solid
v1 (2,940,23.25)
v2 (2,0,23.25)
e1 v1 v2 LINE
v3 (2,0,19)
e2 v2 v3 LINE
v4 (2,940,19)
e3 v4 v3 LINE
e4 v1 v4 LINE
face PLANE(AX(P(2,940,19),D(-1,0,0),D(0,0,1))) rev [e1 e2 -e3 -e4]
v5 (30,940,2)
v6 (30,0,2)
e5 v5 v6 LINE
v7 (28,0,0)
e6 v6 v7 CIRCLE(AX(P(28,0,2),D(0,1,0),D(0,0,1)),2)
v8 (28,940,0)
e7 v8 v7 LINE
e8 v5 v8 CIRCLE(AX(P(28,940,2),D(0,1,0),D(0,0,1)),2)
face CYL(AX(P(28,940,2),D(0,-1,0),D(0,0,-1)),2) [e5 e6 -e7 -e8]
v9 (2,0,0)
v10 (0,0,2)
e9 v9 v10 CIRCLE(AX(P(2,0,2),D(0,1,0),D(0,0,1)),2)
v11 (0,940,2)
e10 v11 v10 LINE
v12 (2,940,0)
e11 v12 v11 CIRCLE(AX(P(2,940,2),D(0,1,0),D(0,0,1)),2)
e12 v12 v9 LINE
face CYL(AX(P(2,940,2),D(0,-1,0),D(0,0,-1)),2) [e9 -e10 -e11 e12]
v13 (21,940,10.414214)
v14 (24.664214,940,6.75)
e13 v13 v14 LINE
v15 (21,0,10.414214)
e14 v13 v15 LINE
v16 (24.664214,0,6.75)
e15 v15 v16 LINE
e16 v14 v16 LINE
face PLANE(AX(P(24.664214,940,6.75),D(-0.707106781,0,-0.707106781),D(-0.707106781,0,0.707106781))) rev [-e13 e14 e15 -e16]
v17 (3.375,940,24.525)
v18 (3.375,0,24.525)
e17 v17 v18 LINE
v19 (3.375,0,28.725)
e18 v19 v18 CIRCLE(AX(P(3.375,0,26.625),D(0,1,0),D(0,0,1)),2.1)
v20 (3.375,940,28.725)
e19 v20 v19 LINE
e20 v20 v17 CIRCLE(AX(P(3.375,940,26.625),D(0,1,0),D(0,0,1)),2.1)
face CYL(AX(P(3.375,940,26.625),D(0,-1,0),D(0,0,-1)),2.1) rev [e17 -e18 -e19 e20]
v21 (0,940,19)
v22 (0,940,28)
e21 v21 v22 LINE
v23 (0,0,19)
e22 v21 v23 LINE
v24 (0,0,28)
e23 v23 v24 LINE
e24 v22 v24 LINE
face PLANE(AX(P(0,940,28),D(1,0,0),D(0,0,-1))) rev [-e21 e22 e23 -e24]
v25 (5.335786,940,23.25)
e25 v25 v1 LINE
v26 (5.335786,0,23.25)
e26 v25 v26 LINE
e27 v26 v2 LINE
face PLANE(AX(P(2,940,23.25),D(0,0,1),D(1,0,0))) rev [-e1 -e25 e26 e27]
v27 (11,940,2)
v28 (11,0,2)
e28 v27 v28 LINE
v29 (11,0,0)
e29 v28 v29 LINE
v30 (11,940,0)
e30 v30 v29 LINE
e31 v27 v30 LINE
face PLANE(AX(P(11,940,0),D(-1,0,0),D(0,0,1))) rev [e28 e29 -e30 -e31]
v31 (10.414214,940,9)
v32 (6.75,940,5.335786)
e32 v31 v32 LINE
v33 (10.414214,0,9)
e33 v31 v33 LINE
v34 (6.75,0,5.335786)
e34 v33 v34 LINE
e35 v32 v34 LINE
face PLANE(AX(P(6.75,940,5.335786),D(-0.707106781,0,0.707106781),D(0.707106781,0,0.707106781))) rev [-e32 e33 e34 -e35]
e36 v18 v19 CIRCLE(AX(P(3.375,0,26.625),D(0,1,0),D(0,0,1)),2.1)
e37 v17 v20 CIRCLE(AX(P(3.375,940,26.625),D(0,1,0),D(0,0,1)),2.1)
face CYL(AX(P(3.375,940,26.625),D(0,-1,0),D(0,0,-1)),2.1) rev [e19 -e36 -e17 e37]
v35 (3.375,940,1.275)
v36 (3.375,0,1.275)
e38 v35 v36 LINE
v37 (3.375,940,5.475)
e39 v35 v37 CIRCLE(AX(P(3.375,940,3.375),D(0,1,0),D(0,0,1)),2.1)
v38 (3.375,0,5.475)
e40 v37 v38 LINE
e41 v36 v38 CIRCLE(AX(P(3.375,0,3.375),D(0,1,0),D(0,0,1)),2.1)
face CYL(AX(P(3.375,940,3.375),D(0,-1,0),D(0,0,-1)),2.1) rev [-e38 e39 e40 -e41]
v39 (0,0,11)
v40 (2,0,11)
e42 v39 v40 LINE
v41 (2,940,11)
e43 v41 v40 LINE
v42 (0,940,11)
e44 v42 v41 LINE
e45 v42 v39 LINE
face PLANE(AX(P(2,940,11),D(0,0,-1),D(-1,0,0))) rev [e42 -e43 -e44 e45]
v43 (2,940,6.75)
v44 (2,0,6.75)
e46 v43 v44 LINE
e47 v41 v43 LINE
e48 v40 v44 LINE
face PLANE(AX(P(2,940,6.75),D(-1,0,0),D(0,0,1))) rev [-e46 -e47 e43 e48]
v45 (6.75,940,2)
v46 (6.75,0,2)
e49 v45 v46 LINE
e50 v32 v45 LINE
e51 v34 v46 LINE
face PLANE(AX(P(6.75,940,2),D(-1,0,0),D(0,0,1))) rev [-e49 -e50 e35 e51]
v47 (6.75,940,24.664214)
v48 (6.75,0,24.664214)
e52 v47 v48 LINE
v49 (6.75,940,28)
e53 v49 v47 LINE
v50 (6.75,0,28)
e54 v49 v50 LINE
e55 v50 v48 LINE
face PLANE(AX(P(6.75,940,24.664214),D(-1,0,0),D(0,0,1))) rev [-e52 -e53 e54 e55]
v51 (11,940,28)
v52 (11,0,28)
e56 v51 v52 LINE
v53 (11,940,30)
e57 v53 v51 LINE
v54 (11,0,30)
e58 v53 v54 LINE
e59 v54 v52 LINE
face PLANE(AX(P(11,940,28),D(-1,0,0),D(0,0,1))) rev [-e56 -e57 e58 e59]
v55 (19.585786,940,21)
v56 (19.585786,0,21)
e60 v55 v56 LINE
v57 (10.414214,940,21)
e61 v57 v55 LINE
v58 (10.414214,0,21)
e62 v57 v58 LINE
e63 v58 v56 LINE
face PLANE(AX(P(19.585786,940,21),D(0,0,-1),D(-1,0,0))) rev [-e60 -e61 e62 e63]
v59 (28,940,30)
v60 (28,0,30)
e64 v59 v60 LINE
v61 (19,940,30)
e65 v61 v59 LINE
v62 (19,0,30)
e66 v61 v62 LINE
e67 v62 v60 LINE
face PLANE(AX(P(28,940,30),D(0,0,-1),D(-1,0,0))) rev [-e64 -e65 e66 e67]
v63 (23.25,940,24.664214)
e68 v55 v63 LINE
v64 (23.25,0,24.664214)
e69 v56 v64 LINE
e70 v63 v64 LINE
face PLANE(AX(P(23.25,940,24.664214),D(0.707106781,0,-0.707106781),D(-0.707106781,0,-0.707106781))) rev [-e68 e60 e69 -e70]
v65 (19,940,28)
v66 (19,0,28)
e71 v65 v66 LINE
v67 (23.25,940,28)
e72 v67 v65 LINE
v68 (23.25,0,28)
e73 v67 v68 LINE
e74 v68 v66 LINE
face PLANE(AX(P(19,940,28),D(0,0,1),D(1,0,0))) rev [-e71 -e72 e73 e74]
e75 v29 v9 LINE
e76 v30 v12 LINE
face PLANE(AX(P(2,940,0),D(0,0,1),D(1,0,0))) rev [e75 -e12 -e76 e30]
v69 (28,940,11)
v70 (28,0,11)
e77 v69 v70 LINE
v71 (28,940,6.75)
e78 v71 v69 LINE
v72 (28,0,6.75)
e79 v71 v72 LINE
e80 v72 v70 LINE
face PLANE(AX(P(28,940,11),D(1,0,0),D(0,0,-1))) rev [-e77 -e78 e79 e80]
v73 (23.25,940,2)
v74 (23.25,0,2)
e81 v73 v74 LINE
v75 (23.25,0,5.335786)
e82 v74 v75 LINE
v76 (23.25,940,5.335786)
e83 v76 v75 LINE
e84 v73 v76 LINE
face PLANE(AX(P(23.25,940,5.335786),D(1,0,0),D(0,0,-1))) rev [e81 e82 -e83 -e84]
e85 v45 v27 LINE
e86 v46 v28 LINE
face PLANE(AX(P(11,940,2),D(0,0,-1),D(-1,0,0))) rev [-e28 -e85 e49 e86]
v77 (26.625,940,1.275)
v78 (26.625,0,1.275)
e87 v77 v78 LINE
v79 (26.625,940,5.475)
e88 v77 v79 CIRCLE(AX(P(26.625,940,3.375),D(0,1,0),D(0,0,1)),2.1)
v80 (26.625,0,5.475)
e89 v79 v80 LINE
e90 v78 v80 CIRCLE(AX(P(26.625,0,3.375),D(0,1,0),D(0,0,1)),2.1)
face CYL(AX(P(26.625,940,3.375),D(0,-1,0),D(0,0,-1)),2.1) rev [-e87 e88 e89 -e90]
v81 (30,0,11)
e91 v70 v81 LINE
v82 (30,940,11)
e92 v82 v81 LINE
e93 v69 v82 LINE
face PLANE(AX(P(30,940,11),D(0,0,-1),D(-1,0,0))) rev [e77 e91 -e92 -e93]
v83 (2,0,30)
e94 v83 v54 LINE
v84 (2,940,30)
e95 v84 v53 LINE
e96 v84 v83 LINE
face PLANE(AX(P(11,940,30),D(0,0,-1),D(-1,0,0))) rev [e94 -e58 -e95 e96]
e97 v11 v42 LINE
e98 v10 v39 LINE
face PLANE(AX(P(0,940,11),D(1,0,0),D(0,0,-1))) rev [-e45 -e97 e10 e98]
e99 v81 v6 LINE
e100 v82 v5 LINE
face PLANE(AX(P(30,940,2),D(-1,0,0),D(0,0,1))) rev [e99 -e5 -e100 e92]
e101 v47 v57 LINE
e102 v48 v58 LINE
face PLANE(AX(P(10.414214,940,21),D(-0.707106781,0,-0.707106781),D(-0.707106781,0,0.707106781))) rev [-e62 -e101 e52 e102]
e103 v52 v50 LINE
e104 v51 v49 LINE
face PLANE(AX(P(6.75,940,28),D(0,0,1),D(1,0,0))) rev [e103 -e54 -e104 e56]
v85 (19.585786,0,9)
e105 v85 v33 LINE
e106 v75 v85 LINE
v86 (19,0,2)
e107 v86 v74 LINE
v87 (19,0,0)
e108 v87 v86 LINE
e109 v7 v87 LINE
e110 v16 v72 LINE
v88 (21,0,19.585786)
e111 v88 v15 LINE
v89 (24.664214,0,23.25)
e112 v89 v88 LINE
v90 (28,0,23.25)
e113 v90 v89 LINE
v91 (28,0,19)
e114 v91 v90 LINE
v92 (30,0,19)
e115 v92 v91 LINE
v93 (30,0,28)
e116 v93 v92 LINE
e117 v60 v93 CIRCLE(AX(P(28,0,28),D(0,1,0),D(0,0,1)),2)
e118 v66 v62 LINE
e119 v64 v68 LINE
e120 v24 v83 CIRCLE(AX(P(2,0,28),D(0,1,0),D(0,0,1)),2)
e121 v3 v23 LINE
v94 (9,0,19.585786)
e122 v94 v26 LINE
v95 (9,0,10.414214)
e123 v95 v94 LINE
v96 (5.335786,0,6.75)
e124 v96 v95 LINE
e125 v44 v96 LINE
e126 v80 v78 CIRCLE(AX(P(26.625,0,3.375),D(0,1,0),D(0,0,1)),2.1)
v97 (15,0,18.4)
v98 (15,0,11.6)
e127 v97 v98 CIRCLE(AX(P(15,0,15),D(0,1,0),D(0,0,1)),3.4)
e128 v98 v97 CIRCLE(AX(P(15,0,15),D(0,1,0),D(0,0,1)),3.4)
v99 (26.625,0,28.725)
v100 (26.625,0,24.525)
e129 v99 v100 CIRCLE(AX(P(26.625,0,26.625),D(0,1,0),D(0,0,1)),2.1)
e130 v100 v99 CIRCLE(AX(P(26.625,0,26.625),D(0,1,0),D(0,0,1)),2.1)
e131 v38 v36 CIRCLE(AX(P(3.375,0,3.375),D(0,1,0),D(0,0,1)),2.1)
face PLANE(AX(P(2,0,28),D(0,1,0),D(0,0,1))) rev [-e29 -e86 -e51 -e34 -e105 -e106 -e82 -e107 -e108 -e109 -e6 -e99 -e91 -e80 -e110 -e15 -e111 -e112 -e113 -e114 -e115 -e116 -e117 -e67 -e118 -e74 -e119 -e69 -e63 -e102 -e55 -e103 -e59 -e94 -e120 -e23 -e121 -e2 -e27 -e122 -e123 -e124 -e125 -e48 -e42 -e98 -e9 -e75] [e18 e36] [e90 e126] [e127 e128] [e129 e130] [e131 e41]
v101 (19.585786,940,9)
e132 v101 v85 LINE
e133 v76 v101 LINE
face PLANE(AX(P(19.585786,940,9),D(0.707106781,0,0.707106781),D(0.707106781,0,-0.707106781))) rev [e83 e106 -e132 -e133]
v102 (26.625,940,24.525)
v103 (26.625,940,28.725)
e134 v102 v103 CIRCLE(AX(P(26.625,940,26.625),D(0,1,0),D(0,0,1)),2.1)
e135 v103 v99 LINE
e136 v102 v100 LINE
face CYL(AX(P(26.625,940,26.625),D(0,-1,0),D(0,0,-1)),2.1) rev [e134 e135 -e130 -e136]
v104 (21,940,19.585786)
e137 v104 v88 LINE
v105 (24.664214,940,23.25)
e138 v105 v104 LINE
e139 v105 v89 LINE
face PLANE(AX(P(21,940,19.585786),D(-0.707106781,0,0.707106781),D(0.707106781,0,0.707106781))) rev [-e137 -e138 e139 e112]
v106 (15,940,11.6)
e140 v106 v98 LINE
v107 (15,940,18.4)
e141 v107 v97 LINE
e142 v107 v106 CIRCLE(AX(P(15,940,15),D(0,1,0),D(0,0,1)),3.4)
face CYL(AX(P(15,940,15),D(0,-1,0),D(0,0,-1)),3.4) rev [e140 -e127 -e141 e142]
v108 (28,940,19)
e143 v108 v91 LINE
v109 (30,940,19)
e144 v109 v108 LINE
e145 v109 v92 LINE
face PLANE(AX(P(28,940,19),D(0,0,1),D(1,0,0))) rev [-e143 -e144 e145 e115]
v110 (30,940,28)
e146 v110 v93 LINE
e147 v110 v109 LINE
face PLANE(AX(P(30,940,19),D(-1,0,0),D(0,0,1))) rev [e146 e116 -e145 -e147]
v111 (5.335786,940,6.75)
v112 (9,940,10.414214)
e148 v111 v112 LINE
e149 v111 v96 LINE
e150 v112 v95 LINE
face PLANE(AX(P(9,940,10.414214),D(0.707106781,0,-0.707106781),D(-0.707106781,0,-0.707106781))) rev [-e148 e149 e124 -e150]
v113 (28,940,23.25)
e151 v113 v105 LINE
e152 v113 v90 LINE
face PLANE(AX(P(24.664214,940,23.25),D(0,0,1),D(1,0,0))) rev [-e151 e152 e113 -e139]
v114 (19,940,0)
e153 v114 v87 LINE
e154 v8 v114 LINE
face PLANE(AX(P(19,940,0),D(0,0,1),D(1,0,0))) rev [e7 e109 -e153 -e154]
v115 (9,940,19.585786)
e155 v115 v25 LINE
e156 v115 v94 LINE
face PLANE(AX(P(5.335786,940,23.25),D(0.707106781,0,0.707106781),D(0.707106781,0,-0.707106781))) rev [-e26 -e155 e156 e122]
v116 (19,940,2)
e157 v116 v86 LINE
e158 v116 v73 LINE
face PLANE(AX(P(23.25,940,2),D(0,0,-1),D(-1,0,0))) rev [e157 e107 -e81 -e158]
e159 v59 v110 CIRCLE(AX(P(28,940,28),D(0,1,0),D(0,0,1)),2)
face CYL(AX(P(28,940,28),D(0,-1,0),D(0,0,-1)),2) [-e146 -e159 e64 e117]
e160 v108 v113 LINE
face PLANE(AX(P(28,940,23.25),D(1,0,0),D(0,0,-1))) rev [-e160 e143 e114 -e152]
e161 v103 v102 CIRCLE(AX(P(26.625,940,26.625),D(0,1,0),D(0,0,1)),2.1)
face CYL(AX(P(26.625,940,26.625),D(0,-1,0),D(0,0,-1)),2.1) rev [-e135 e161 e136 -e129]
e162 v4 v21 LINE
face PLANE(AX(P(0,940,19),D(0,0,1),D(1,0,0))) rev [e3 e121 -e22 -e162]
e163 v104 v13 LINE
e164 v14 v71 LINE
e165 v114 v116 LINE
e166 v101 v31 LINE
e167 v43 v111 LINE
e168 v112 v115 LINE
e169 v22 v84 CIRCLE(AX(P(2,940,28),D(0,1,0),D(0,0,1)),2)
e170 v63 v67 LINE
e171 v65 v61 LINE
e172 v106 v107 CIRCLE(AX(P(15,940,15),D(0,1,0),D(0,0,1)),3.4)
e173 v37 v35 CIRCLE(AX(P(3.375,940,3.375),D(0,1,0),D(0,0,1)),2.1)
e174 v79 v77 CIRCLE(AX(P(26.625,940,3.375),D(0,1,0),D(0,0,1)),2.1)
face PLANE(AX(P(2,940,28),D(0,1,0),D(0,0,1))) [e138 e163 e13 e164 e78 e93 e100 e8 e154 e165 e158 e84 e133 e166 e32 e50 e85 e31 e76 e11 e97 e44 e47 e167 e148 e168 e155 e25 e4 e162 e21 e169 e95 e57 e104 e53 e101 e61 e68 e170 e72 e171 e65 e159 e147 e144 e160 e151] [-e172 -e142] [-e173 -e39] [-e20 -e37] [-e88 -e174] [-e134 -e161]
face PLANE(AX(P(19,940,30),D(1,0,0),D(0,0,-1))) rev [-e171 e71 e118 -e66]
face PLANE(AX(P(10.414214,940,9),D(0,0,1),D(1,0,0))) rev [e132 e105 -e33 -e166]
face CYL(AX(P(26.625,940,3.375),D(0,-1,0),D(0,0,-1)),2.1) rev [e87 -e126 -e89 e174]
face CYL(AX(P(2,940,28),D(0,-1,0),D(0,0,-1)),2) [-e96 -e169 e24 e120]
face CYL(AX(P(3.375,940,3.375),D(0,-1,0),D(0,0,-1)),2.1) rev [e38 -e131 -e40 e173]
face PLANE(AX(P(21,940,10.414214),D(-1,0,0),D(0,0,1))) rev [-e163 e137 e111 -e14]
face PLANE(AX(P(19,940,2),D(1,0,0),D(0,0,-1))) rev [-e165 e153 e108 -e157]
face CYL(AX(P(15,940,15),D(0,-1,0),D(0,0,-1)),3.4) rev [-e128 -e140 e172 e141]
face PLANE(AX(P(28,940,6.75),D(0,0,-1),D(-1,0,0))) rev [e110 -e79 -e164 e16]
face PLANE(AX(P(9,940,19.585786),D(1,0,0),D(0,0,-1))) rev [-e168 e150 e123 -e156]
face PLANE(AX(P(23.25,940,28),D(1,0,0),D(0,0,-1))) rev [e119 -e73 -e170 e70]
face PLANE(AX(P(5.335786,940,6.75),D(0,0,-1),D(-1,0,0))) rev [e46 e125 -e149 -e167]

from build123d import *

# Parameters (mm, degrees)
SKETCH_1_R      = 2.1
SKETCH_1_R_2    = 3.4
EXTRUDE_1_DEPTH = 940


with BuildPart() as part:
    # 草图1 → 拉伸1 (new body)
    with BuildSketch(Plane(origin=(0, 0, 0), x_dir=(1, 0, 0), z_dir=(0, 1, 0))):
        with BuildLine():
            Line((6.75, -28), (11, -28))
            Line((11, -28), (11, -30))
            Line((11, -30), (2, -30))
            ThreePointArc((2, -30), (0.585786438, -29.414213562), (0, -28))
            Line((0, -28), (0, -19))
            Line((0, -19), (2, -19))
            Line((2, -19), (2, -23.25))
            Line((2, -23.25), (5.335785999, -23.25))
            Line((5.335785999, -23.25), (9, -19.585785999))
            Line((9, -19.585785999), (9, -10.414214001))
            Line((9, -10.414214001), (5.335785999, -6.75))
            Line((5.335785999, -6.75), (2, -6.75))
            Line((2, -6.75), (2, -11))
            Line((2, -11), (0, -11))
            Line((0, -11), (0, -2))
            ThreePointArc((0, -2), (0.585786438, -0.585786438), (2, 0))
            Line((2, 0), (11, 0))
            Line((11, 0), (11, -2))
            Line((11, -2), (6.75, -2))
            Line((6.75, -2), (6.75, -5.335785999))
            Line((6.75, -5.335785999), (10.414214001, -9))
            Line((10.414214001, -9), (19.585785999, -9))
            Line((19.585785999, -9), (23.25, -5.335785999))
            Line((23.25, -5.335785999), (23.25, -2))
            Line((23.25, -2), (19, -2))
            Line((19, -2), (19, 0))
            Line((19, 0), (28, 0))
            ThreePointArc((28, 0), (29.414213562, -0.585786438), (30, -2))
            Line((30, -2), (30, -11))
            Line((30, -11), (28, -11))
            Line((28, -11), (28, -6.75))
            Line((28, -6.75), (24.664214001, -6.75))
            Line((24.664214001, -6.75), (21, -10.414214001))
            Line((21, -10.414214001), (21, -19.585785999))
            Line((21, -19.585785999), (24.664214001, -23.25))
            Line((24.664214001, -23.25), (28, -23.25))
            Line((28, -23.25), (28, -19))
            Line((28, -19), (30, -19))
            Line((30, -19), (30, -28))
            ThreePointArc((30, -28), (29.414213562, -29.414213562), (28, -30))
            Line((28, -30), (19, -30))
            Line((19, -30), (19, -28))
            Line((19, -28), (23.25, -28))
            Line((23.25, -28), (23.25, -24.664214001))
            Line((23.25, -24.664214001), (19.585785999, -21))
            Line((19.585785999, -21), (10.414214001, -21))
            Line((10.414214001, -21), (6.75, -24.664214001))
            Line((6.75, -24.664214001), (6.75, -28))
        make_face()
        with Locations(Location((3.375, -26.625, 0), (0, 0, 90))):
            Circle(SKETCH_1_R, mode=Mode.SUBTRACT)
        with Locations(Location((26.625, -26.625, 0), (0, 0, 90))):
            Circle(SKETCH_1_R, mode=Mode.SUBTRACT)
        with Locations(Location((15, -15, 0), (0, 0, 90))):
            Circle(SKETCH_1_R_2, mode=Mode.SUBTRACT)
        with Locations(Location((3.375, -3.375, 0), (0, 0, 90))):
            Circle(SKETCH_1_R, mode=Mode.SUBTRACT)
        with Locations(Location((26.625, -3.375, 0), (0, 0, 90))):
            Circle(SKETCH_1_R, mode=Mode.SUBTRACT)
    extrude(amount=EXTRUDE_1_DEPTH)


solid = part.part
